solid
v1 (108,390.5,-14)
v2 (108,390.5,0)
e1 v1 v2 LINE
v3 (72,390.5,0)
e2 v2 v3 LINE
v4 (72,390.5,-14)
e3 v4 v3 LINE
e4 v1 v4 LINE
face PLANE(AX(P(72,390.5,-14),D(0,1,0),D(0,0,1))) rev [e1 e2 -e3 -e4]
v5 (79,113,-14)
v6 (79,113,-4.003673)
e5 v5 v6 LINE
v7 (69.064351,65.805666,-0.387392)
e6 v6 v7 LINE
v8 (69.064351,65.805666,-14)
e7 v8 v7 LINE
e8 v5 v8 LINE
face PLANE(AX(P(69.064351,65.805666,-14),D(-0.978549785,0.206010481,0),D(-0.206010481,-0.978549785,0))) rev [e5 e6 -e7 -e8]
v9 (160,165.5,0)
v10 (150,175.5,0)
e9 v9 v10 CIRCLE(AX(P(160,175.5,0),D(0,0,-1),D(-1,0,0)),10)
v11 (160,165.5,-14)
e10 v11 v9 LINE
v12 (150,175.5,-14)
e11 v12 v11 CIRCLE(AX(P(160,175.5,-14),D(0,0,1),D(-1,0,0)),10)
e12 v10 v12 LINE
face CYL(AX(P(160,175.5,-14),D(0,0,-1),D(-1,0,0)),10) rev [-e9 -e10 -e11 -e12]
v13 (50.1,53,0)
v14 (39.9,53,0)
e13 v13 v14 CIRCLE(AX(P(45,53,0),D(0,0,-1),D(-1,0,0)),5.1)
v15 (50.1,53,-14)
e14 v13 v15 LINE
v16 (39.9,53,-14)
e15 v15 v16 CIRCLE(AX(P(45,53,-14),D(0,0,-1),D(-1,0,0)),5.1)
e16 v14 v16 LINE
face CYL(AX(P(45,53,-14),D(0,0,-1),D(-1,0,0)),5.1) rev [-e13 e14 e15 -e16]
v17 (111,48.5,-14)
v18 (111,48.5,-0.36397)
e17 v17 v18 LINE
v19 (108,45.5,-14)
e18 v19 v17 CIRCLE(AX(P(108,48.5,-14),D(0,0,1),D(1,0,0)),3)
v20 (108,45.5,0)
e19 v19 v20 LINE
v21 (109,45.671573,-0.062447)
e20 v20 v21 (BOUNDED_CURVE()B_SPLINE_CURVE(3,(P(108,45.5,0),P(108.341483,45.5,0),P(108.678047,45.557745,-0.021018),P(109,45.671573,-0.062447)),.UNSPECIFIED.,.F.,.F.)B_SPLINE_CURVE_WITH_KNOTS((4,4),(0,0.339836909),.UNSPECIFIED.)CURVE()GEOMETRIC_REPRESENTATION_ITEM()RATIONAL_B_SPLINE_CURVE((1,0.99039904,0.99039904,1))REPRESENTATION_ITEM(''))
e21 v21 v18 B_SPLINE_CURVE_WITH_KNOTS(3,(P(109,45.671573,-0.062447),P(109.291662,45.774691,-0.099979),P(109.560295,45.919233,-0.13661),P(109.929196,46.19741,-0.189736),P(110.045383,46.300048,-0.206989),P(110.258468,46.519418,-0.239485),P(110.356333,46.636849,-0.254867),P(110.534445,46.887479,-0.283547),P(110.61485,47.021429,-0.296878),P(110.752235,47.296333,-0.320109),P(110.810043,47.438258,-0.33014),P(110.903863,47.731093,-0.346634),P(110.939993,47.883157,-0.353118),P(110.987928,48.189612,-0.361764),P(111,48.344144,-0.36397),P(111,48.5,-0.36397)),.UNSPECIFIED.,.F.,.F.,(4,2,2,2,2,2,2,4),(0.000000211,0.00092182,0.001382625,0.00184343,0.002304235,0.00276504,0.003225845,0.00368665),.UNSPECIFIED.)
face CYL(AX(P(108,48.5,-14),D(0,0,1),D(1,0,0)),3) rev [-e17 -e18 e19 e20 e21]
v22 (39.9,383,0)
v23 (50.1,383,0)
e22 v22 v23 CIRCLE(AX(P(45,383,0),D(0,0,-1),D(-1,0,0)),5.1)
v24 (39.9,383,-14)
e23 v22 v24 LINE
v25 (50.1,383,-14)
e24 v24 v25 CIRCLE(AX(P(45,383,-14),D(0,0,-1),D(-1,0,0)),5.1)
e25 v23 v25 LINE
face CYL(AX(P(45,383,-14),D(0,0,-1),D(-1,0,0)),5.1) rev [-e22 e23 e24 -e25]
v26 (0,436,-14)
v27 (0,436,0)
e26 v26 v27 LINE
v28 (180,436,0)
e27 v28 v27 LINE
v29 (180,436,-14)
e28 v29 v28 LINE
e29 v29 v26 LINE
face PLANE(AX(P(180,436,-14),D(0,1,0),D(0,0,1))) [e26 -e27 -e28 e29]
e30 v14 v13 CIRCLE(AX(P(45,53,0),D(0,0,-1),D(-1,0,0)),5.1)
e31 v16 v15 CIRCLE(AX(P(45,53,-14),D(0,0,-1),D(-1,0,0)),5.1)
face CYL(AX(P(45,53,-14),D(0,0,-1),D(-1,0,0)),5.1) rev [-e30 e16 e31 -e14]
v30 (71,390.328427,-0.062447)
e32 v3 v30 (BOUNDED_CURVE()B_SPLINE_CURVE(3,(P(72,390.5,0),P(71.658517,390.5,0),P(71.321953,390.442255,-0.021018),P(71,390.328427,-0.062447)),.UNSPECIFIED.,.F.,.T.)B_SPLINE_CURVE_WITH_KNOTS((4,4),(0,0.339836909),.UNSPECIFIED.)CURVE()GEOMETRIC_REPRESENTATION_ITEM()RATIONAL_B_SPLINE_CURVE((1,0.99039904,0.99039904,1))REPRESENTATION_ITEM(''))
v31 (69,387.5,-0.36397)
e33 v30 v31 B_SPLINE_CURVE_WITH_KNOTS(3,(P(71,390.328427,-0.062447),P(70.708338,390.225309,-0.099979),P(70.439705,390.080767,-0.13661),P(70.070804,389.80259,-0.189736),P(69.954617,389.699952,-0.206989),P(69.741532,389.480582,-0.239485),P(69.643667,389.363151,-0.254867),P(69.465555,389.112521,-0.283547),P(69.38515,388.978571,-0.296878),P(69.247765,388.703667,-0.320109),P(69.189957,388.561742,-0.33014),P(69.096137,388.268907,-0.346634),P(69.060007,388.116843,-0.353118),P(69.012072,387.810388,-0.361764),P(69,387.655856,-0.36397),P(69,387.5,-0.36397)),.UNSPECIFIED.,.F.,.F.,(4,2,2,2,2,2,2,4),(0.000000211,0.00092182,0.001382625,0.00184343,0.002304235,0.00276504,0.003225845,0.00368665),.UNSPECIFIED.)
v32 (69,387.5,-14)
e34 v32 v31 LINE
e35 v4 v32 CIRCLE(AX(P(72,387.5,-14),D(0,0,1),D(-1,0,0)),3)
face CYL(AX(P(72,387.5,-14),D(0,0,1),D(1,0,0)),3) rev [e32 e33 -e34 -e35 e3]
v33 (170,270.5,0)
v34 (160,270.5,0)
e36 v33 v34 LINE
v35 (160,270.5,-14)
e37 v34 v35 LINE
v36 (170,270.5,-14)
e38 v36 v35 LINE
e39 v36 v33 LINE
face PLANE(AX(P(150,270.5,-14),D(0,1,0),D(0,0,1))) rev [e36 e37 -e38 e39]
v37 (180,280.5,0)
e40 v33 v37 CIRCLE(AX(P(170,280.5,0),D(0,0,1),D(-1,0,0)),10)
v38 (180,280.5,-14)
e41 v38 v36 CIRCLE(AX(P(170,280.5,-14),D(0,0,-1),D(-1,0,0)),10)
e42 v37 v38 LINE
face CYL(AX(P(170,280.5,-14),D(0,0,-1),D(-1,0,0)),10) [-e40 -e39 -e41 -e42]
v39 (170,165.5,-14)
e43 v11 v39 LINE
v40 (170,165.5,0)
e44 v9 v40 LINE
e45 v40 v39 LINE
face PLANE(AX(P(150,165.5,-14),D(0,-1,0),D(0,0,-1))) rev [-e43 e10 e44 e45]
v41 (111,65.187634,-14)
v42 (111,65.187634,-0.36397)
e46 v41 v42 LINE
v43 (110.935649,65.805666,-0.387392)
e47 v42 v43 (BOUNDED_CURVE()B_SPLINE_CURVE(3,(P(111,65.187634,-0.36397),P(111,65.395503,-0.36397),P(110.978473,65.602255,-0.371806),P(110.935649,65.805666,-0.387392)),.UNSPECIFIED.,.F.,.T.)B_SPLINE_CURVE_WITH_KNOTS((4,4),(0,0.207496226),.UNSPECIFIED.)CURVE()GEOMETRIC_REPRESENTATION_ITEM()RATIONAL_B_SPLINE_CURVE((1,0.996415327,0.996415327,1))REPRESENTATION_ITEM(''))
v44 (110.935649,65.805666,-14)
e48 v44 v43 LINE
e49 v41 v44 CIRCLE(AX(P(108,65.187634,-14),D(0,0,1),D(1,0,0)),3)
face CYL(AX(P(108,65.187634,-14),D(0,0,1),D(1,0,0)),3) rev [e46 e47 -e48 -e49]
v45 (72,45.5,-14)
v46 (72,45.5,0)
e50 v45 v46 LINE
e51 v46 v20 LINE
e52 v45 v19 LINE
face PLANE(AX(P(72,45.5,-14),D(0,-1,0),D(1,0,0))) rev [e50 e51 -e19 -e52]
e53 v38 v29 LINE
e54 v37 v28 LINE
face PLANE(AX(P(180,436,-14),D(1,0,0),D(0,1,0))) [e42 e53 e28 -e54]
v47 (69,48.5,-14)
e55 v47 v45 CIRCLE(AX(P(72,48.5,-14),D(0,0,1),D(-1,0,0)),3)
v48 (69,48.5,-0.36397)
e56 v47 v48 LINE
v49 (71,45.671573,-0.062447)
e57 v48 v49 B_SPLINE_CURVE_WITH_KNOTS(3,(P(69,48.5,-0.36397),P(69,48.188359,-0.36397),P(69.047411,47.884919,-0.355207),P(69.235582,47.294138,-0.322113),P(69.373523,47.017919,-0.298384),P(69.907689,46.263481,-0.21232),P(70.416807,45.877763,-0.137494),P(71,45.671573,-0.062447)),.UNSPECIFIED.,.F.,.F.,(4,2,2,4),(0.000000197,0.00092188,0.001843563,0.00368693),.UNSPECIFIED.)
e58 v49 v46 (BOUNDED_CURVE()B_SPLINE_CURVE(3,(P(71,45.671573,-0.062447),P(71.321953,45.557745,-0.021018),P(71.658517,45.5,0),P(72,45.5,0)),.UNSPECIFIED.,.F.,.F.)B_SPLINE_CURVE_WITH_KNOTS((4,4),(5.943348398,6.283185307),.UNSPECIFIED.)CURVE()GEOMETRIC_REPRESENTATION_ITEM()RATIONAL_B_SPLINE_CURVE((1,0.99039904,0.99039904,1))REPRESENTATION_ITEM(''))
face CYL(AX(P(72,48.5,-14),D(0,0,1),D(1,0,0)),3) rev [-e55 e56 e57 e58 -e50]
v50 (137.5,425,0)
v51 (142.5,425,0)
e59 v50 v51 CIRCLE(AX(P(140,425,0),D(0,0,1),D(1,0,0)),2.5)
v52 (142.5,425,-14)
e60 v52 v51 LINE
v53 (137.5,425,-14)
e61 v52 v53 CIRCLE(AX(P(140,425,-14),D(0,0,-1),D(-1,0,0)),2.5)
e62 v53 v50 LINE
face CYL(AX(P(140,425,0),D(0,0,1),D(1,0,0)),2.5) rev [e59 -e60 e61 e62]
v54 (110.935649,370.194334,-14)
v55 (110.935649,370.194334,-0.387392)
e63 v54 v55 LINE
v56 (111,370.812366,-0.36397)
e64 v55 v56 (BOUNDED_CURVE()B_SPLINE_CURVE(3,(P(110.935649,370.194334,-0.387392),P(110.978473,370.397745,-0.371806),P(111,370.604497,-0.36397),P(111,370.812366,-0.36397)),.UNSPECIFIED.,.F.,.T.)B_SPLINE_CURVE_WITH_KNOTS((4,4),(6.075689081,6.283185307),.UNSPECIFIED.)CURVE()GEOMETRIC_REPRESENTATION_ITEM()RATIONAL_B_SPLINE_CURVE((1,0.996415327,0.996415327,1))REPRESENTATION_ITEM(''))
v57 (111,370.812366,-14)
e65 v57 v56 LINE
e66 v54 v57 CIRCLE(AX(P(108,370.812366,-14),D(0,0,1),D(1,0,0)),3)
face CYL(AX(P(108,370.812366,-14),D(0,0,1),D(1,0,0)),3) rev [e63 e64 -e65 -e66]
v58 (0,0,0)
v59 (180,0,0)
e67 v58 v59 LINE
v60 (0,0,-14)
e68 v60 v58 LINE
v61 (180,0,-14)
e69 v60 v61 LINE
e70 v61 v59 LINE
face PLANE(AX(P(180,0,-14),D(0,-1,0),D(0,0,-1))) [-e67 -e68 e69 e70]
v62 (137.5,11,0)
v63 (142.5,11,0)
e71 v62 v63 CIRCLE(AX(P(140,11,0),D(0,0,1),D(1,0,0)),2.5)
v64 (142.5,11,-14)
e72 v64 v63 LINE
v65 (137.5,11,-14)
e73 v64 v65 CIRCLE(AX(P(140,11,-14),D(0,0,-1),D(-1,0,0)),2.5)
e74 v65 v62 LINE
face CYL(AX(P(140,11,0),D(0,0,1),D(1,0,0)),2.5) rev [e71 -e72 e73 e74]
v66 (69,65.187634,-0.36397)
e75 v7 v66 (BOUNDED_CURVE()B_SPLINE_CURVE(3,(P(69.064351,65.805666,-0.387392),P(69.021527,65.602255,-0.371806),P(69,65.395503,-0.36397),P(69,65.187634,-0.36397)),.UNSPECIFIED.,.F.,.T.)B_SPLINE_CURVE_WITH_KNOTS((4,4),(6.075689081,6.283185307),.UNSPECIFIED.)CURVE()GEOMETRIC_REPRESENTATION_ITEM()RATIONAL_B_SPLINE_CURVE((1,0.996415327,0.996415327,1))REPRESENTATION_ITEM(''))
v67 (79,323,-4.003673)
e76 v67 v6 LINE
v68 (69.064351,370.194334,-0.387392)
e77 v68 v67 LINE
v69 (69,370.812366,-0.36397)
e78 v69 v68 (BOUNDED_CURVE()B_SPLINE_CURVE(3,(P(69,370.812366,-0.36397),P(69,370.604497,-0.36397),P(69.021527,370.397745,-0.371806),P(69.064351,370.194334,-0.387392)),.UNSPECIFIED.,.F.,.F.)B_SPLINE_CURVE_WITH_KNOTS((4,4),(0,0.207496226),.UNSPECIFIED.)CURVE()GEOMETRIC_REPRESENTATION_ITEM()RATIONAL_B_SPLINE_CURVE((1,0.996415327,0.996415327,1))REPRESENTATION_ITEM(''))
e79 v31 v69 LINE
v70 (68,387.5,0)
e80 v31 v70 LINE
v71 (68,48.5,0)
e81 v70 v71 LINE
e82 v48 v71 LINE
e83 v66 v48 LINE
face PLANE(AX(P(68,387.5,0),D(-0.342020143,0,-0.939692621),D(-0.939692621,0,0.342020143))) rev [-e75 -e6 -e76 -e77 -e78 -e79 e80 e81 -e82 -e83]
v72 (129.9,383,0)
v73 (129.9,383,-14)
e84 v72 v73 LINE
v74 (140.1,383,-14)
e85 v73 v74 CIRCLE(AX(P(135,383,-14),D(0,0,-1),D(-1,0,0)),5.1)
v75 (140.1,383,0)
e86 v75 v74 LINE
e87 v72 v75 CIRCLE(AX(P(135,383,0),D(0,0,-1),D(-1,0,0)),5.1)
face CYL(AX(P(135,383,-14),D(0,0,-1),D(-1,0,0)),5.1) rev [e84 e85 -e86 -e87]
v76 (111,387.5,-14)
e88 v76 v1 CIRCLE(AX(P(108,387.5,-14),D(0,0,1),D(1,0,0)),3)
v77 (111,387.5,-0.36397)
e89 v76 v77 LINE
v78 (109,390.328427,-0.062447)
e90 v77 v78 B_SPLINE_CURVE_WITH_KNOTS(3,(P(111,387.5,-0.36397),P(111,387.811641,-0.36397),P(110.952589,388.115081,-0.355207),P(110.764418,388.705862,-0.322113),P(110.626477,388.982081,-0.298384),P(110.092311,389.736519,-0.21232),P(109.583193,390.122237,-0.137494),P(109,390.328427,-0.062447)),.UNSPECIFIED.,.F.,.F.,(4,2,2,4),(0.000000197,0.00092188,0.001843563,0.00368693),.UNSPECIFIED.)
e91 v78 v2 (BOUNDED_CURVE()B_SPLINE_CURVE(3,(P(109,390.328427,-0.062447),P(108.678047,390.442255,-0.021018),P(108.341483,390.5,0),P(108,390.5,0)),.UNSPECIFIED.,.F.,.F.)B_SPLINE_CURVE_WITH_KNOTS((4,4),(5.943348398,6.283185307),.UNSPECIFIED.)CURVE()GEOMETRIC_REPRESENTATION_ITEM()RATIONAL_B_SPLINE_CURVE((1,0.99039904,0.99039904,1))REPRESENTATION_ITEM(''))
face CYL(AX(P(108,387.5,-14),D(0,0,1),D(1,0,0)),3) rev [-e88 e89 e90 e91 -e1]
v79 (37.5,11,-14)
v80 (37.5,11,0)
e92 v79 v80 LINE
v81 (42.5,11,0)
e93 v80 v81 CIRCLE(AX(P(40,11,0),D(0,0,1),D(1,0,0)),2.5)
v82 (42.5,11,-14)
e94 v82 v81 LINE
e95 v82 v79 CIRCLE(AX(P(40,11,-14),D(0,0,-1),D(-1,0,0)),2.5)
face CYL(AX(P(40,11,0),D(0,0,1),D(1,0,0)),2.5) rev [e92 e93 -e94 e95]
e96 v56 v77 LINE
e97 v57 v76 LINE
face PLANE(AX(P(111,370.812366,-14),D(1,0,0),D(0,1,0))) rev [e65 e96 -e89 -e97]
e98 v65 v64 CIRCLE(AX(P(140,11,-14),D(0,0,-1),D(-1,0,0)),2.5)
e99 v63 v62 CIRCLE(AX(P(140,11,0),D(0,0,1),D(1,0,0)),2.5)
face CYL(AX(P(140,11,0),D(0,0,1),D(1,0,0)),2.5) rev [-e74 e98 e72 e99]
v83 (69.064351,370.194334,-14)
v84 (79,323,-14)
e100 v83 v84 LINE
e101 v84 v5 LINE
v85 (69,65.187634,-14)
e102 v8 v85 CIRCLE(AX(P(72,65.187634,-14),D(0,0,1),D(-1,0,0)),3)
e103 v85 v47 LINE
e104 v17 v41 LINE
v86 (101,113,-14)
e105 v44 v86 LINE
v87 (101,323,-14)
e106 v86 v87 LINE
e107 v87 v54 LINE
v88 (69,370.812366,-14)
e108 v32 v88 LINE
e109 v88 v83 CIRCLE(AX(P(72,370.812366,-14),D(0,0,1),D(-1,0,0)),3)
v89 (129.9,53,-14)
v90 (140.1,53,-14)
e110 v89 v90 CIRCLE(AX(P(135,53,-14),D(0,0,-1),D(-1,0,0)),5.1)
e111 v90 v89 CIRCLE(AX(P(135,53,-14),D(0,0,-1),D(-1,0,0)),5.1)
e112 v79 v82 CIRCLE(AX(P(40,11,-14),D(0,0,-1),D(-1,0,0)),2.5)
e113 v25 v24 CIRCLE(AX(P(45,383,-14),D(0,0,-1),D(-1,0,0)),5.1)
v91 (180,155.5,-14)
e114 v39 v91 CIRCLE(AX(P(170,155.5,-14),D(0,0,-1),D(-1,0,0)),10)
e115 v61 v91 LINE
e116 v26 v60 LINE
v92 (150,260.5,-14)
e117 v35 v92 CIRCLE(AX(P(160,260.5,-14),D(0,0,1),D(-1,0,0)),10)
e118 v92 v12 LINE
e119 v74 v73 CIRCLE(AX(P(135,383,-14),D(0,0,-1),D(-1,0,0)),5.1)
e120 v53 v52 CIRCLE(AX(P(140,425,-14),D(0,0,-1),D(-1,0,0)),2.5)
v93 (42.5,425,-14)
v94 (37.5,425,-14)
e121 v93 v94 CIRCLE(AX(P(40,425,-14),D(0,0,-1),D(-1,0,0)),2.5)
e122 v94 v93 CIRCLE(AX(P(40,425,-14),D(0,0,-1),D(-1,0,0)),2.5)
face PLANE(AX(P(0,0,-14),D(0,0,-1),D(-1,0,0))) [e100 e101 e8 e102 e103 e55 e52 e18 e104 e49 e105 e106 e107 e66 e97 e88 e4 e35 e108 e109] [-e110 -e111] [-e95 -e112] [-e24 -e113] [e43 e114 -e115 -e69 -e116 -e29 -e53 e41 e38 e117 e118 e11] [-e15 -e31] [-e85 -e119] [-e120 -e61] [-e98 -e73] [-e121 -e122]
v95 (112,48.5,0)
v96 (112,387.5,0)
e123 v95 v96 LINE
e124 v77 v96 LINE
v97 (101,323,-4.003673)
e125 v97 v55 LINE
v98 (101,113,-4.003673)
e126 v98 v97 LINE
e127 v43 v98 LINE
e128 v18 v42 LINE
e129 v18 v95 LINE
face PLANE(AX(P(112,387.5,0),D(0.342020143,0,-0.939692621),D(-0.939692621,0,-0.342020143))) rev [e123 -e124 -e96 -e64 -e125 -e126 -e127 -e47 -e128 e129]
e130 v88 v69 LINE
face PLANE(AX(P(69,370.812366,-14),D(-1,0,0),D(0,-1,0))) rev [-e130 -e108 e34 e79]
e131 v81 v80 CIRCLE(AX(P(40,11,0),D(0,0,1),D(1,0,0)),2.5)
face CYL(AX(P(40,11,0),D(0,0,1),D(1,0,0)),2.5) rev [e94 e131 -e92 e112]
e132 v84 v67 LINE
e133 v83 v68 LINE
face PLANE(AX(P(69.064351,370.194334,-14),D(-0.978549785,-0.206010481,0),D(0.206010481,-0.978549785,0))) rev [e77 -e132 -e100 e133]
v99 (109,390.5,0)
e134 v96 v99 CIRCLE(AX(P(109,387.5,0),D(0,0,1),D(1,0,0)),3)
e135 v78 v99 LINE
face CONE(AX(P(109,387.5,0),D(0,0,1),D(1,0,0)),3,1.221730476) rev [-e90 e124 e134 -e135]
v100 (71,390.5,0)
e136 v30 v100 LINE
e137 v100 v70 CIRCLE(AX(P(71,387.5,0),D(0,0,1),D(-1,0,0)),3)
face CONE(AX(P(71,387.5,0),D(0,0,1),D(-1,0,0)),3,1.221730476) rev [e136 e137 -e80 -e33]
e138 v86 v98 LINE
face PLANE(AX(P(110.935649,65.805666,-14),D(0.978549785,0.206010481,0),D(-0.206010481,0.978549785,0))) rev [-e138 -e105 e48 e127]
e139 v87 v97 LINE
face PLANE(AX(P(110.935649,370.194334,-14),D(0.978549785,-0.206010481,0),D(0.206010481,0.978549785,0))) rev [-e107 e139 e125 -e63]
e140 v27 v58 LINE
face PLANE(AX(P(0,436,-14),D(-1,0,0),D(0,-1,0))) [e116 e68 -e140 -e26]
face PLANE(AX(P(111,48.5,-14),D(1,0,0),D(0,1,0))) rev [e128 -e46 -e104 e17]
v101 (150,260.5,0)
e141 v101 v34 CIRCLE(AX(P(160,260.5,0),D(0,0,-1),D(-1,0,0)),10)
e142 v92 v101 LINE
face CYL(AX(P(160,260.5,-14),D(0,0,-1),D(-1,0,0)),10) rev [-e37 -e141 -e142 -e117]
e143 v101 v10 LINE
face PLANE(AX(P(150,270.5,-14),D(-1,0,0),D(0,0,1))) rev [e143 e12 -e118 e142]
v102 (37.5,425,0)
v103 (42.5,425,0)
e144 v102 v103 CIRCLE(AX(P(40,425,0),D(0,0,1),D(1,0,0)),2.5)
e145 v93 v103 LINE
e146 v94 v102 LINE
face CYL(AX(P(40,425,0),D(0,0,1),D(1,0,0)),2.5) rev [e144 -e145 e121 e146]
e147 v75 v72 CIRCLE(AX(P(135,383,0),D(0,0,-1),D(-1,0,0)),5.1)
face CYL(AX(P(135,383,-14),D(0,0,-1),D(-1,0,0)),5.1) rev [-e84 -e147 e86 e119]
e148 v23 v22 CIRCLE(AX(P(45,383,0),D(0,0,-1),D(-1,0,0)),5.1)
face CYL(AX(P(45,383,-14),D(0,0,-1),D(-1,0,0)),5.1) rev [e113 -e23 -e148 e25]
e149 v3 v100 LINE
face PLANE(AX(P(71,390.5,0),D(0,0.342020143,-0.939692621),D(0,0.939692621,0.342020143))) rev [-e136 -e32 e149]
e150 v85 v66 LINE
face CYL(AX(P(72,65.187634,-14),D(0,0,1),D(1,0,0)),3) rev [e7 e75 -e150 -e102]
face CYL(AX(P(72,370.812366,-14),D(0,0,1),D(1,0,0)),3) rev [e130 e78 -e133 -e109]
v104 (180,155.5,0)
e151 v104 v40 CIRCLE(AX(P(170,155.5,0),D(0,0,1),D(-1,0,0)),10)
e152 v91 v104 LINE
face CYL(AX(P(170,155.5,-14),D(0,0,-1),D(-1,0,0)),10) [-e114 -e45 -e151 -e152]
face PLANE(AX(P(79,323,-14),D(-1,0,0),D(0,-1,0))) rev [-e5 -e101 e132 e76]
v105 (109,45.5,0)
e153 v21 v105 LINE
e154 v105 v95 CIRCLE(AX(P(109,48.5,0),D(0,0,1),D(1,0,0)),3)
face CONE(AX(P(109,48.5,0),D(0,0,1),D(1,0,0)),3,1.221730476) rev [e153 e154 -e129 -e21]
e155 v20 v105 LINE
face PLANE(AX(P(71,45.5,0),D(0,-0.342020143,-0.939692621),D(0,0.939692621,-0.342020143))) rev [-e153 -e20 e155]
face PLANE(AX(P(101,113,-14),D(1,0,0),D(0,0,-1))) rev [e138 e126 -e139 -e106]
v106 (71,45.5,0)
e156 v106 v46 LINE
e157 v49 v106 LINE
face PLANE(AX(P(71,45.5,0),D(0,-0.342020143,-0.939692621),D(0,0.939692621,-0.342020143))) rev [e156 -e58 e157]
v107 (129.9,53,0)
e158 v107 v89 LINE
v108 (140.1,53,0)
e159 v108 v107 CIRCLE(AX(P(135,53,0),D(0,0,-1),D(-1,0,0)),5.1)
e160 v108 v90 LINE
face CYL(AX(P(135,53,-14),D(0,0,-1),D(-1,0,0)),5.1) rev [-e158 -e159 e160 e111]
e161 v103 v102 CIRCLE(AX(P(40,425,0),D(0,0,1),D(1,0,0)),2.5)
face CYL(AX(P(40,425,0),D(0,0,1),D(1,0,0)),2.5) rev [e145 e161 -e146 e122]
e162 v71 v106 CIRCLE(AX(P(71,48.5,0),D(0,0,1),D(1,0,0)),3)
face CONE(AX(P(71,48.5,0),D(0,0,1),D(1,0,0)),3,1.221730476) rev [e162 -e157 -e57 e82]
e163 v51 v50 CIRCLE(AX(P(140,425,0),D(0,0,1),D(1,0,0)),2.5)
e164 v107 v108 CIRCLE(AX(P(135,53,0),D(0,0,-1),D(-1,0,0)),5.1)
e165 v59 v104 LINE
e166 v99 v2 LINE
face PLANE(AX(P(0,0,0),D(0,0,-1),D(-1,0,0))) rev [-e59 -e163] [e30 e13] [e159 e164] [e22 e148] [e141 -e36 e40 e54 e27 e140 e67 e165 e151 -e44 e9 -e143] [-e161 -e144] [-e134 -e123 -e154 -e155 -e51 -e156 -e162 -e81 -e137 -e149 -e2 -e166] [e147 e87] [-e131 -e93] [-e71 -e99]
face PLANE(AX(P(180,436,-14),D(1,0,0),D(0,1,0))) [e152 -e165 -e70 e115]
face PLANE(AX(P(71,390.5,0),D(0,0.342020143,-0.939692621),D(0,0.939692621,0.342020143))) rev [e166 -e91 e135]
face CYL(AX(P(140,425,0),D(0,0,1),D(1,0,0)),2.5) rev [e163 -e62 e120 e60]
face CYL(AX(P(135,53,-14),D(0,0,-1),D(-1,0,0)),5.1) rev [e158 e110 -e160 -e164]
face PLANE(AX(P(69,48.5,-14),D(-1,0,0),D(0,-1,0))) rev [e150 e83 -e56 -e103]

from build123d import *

# Parameters (mm, degrees)
SKETCH1_W              = 180
SKETCH1_H              = 436
BOSS_EXTRUDE1_DEPTH    = 14
SKETCH5_W              = 30
SKETCH5_H              = 105
CUT_EXTRUDE1_DEPTH     = 472.902532309
M12_TAPPED_HOLE1_D     = 10.2
M12_TAPPED_HOLE1_DEPTH = 32.75
M12_TAPPED_HOLE1_TIP   = 3.064389157
FILLET1_R              = 10
M6_TAPPED_HOLE1_D      = 5
M6_TAPPED_HOLE1_DEPTH  = 17
M6_TAPPED_HOLE1_TIP    = 1.502151548
CUT_EXTRUDE2_DEPTH     = 5
CUT_EXTRUDE2_DRAFT     = -70


with BuildPart() as part:
    # Sketch1 → Boss-Extrude1 (new body)
    with BuildSketch(Plane.XY):
        with Locations((90, 218)):
            Rectangle(SKETCH1_W, SKETCH1_H)
        with BuildLine():
            Line((72, 45.5), (108, 45.5))
            ThreePointArc((108, 45.5), (110.121320344, 46.378679656), (111, 48.5))
            Line((111, 48.5), (111, 65.187634121))
            ThreePointArc((111, 65.187634121), (110.98386897, 65.498320406), (110.935649355, 65.805665564))
            Line((110.935649355, 65.805665564), (101, 113))
            Line((101, 113), (101, 323))
            Line((101, 323), (110.935649355, 370.194334436))
            ThreePointArc((110.935649355, 370.194334436), (110.98386897, 370.501679594), (111, 370.812365879))
            Line((111, 370.812365879), (111, 387.5))
            ThreePointArc((111, 387.5), (110.121320344, 389.621320344), (108, 390.5))
            Line((108, 390.5), (72, 390.5))
            ThreePointArc((72, 390.5), (69.878679656, 389.621320344), (69, 387.5))
            Line((69, 387.5), (69, 370.812365879))
            ThreePointArc((69, 370.812365879), (69.01613103, 370.501679594), (69.064350645, 370.194334436))
            Line((69.064350645, 370.194334436), (79, 323))
            Line((79, 323), (79, 113))
            Line((79, 113), (69.064350645, 65.805665564))
            ThreePointArc((69.064350645, 65.805665564), (69.01613103, 65.498320406), (69, 65.187634121))
            Line((69, 65.187634121), (69, 48.5))
            ThreePointArc((69, 48.5), (69.878679656, 46.378679656), (72, 45.5))
        make_face(mode=Mode.SUBTRACT)
    extrude(amount=-BOSS_EXTRUDE1_DEPTH)

    # Sketch5 → Cut-Extrude1 (cut, through all)
    with BuildSketch(Plane.XY):
        with Locations((165, 218)):
            Rectangle(SKETCH5_W, SKETCH5_H)
    extrude(amount=-CUT_EXTRUDE1_DEPTH, mode=Mode.SUBTRACT)

    # M12 Tapped Hole1
    with Locations(Plane(origin=(0, 0, -14), x_dir=(-1, 0, 0), z_dir=(0, 0, -1))):
        with Locations((-135, 383), (-45, 383), (-45, 53), (-135, 53)):
            Hole(M12_TAPPED_HOLE1_D / 2, depth=M12_TAPPED_HOLE1_DEPTH)
            with Locations((0, 0, -(M12_TAPPED_HOLE1_DEPTH + M12_TAPPED_HOLE1_TIP / 2))):  # 118° drill point
                Cone(0, M12_TAPPED_HOLE1_D / 2, M12_TAPPED_HOLE1_TIP, mode=Mode.SUBTRACT)

    # Fillet1
    fillet1_edges = [part.edges().sort_by_distance(p)[0] for p in [
        (150, 165.5, -7),
        (150, 270.5, -7),
        (180, 270.5, -7),
        (180, 165.5, -7),
    ]]
    fillet(fillet1_edges, radius=FILLET1_R)

    # M6 Tapped Hole1
    with Locations(Plane.XY):
        with Locations((40, 425), (140, 425), (40, 11), (140, 11)):
            Hole(M6_TAPPED_HOLE1_D / 2, depth=M6_TAPPED_HOLE1_DEPTH)
            with Locations((0, 0, -(M6_TAPPED_HOLE1_DEPTH + M6_TAPPED_HOLE1_TIP / 2))):  # 118° drill point
                Cone(0, M6_TAPPED_HOLE1_D / 2, M6_TAPPED_HOLE1_TIP, mode=Mode.SUBTRACT)


with BuildPart() as cut_extrude2_tool:
    # Sketch8 → Cut-Extrude2 (with draft: the straight prism first)
    with BuildSketch(Plane.XY):
        with BuildLine():
            ThreePointArc((71, 390.5), (68.878679656, 389.621320344), (68, 387.5))
            Line((68, 387.5), (68, 48.5))
            ThreePointArc((68, 48.5), (68.878679656, 46.378679656), (71, 45.5))
            Line((71, 45.5), (109, 45.5))
            ThreePointArc((109, 45.5), (111.121320344, 46.378679656), (112, 48.5))
            Line((112, 48.5), (112, 387.5))
            ThreePointArc((112, 387.5), (111.121320344, 389.621320344), (109, 390.5))
            Line((109, 390.5), (71, 390.5))
        make_face()
    extrude(amount=-CUT_EXTRUDE2_DEPTH)
    # Cut-Extrude2: the draft: its side faces are tilted about the plane it starts from
    cut_extrude2_sides = [cut_extrude2_tool.faces().sort_by_distance(p)[0] for p in [
        (111.121320344, 389.621320344, -2.5),
        (90, 390.5, -2.5),
        (68.878679656, 389.621320344, -2.5),
        (68, 218, -2.5),
        (68.878679656, 46.378679656, -2.5),
        (90, 45.5, -2.5),
        (111.121320344, 46.378679656, -2.5),
        (112, 218, -2.5),
    ]]
    draft(cut_extrude2_sides, Plane.XY, CUT_EXTRUDE2_DRAFT)


with BuildPart() as part_1:
    add(part.part)

    # Cut-Extrude2: cut by cut_extrude2_tool
    add(cut_extrude2_tool.part, mode=Mode.SUBTRACT)


solid = part_1.part
